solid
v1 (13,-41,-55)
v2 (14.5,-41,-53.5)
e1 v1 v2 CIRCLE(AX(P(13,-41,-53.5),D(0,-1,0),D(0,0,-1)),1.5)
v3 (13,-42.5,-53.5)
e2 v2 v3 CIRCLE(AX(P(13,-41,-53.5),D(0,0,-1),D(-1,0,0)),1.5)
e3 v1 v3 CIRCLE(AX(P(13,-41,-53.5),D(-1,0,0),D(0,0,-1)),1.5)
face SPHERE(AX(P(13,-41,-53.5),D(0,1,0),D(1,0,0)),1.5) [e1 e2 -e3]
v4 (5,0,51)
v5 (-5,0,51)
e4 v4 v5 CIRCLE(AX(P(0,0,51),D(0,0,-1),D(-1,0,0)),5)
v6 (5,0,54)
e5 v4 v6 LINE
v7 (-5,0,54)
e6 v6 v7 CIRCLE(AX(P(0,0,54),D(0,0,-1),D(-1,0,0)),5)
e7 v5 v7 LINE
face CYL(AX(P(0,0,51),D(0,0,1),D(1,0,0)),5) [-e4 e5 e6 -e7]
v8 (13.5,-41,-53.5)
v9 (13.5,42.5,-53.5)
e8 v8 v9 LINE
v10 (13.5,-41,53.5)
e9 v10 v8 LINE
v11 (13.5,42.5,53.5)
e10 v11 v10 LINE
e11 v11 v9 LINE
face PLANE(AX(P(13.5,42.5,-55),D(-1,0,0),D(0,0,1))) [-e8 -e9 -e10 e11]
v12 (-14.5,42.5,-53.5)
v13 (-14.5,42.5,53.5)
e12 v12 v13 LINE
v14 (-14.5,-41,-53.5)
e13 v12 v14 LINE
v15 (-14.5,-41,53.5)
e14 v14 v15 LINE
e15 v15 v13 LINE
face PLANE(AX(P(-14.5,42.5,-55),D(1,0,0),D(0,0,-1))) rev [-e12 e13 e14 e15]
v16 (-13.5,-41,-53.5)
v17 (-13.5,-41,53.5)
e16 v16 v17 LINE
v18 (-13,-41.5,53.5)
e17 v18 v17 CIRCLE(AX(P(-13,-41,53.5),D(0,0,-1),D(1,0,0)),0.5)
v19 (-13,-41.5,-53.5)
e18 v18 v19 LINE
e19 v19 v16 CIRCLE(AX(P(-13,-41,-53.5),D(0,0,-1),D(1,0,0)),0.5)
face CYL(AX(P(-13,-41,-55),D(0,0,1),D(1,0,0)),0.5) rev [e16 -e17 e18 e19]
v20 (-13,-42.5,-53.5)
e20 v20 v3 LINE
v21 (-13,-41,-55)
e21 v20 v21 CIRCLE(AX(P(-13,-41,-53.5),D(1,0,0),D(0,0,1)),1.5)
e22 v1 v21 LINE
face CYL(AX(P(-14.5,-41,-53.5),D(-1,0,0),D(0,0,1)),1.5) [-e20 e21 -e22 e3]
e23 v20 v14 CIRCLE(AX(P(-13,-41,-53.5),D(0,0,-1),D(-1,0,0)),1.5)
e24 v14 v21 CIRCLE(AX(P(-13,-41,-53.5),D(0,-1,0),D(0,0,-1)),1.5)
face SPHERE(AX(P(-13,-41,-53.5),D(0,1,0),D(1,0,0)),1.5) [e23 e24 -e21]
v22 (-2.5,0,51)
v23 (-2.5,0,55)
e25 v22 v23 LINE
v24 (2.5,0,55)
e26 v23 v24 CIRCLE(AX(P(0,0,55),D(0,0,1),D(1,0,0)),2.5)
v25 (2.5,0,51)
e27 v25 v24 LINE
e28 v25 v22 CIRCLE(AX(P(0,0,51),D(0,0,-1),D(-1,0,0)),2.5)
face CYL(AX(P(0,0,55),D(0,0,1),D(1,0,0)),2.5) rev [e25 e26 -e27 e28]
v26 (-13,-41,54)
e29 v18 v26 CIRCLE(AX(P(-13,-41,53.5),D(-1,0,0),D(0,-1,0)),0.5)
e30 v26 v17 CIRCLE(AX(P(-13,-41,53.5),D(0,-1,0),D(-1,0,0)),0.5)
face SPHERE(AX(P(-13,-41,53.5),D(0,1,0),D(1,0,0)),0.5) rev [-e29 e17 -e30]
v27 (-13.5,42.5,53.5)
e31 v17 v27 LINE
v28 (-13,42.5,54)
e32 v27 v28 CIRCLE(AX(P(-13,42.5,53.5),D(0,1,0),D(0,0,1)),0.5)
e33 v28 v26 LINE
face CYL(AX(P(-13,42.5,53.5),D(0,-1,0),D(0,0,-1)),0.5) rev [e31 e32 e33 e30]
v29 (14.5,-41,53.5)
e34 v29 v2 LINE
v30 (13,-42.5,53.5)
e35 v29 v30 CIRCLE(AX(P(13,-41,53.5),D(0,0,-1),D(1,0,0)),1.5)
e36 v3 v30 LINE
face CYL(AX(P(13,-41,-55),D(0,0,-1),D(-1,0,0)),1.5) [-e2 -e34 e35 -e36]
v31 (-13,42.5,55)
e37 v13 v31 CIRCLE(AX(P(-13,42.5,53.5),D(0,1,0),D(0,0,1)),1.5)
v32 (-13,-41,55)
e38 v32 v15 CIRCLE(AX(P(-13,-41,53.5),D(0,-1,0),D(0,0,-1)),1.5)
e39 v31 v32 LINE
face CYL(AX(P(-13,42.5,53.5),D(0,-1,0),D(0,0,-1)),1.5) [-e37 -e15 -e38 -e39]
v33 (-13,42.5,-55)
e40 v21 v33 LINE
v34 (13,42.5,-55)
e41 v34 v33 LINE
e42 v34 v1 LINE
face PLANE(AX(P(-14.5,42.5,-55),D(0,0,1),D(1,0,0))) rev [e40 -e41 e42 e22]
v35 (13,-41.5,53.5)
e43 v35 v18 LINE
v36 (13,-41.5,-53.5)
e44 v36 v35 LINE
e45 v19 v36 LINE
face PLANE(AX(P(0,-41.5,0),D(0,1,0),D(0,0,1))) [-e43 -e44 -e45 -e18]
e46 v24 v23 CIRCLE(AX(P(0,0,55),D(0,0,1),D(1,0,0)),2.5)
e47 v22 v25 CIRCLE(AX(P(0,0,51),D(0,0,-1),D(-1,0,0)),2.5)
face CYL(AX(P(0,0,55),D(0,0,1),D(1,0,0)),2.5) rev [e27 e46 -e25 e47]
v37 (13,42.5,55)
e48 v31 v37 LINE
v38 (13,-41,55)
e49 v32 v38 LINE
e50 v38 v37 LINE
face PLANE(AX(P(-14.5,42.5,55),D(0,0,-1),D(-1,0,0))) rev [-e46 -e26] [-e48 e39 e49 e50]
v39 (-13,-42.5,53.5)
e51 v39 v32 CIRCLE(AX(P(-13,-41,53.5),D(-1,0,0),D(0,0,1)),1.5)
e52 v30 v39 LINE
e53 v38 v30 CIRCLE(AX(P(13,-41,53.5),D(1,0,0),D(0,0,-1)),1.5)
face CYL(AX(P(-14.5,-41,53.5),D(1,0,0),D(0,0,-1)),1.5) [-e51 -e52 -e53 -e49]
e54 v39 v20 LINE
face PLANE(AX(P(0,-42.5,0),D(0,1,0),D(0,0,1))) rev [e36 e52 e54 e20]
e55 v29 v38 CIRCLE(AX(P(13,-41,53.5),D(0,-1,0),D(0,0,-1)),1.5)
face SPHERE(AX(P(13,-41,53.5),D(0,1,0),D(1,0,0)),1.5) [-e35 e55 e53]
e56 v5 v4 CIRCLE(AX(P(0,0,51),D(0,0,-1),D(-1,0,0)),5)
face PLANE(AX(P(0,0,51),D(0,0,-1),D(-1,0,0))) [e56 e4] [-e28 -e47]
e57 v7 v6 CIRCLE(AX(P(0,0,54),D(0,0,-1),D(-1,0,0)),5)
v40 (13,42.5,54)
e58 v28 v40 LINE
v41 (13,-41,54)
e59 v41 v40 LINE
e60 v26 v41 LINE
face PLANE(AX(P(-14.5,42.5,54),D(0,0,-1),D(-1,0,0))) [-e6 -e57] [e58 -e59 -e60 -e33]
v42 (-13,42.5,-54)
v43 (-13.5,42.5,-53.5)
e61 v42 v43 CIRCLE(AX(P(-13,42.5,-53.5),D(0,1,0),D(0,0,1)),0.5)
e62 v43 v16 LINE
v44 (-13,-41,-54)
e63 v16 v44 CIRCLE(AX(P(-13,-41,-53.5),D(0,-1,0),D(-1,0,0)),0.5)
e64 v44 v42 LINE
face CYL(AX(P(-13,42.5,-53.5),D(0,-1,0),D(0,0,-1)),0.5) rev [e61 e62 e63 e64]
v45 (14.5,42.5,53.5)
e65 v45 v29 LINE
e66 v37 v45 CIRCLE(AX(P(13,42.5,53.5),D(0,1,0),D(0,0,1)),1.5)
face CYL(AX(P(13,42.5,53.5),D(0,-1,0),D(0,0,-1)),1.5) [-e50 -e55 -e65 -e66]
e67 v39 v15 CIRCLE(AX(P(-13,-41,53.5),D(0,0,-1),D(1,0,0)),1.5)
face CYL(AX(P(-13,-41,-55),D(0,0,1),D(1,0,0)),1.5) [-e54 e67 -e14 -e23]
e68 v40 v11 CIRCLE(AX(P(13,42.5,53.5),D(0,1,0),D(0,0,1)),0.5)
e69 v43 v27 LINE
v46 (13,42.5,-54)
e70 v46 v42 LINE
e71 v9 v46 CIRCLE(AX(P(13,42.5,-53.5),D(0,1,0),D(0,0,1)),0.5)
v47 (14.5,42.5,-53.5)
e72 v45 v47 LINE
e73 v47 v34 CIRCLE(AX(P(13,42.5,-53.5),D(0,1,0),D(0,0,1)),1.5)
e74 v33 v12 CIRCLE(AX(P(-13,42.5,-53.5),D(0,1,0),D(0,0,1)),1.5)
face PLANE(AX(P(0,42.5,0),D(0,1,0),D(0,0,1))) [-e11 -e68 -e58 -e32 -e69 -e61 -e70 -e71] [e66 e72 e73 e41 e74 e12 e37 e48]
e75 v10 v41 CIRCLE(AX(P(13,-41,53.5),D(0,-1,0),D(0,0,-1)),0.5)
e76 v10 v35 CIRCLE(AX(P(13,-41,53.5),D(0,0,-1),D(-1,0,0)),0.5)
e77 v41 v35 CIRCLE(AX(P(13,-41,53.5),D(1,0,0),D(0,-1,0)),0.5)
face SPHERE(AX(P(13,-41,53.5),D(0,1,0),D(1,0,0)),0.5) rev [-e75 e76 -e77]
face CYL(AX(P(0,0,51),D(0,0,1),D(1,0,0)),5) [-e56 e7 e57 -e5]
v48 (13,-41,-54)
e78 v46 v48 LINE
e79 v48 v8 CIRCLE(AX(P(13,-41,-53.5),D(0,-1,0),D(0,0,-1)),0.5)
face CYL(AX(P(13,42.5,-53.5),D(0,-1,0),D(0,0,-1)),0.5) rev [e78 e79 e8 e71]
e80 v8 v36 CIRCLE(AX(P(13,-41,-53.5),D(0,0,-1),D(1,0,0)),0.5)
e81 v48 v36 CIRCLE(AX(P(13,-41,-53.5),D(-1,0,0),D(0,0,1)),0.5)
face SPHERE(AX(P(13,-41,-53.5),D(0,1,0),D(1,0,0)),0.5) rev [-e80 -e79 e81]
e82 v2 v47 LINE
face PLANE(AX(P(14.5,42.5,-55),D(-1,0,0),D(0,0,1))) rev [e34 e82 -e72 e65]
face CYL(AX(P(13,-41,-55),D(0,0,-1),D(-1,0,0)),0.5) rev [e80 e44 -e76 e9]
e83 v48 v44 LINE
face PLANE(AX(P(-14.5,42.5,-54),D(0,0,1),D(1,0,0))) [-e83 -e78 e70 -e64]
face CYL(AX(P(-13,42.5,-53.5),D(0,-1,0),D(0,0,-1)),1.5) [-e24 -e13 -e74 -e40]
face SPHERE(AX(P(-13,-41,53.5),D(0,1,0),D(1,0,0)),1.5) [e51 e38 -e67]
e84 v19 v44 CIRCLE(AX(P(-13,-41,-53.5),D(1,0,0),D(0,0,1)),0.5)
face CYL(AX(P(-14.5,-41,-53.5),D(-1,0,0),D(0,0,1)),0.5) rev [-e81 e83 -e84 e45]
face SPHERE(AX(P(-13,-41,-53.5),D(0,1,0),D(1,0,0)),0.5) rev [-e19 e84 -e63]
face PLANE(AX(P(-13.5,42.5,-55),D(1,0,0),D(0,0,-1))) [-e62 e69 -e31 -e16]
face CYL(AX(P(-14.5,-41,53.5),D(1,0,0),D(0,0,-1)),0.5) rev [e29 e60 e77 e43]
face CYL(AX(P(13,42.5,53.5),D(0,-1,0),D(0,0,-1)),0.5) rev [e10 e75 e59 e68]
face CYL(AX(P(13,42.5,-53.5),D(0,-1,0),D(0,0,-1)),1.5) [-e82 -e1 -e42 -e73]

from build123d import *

# Parameters (mm, degrees)
SKETCH1_W             = 29
SKETCH1_H             = 110
BOSS_EXTRUDE1_DEPTH   = 42.5
FILLET1_R             = 1.5
SHELL1_T              = -1
SKETCH2_R             = 5
BOSS_EXTRUDE2_DEPTH   = 3
M6_TAPPED_HOLE1_D     = 5
M6_TAPPED_HOLE1_DEPTH = 4


with BuildPart() as part:
    # Sketch1 → Boss-Extrude1 (new, symmetric)
    with BuildSketch(Plane(origin=(0, 0, 0), x_dir=(1, 0, 0), z_dir=(0, 1, 0))):
        Rectangle(SKETCH1_W, SKETCH1_H)
    extrude(amount=BOSS_EXTRUDE1_DEPTH, both=True)

    # Fillet1
    fillet1_edges = [part.edges().sort_by_distance(p)[0] for p in [
        (0, -42.5, 55),
        (-14.5, -42.5, 0),
        (0, -42.5, -55),
        (14.5, -42.5, 0),
        (14.5, 0, 55),
        (-14.5, 0, 55),
        (-14.5, 0, -55),
        (14.5, 0, -55),
    ]]
    fillet(fillet1_edges, radius=FILLET1_R)

    # Shell1
    shell1_openings = [part.faces().sort_by_distance(p)[0] for p in [
        (0, 42.5, 0),
    ]]
    offset(amount=SHELL1_T, openings=shell1_openings, kind=Kind.INTERSECTION)

    # Sketch2 → Boss-Extrude2 (add)
    with BuildSketch(Plane(origin=(0, 0, 54), x_dir=(-1, 0, 0), z_dir=(0, 0, -1))):
        Circle(SKETCH2_R)
    extrude(amount=BOSS_EXTRUDE2_DEPTH)

    # M6 Tapped Hole1
    with Locations(Plane.XY.offset(55)):
        with Locations((0, 0)):
            Hole(M6_TAPPED_HOLE1_D / 2, depth=M6_TAPPED_HOLE1_DEPTH)


solid = part.part
